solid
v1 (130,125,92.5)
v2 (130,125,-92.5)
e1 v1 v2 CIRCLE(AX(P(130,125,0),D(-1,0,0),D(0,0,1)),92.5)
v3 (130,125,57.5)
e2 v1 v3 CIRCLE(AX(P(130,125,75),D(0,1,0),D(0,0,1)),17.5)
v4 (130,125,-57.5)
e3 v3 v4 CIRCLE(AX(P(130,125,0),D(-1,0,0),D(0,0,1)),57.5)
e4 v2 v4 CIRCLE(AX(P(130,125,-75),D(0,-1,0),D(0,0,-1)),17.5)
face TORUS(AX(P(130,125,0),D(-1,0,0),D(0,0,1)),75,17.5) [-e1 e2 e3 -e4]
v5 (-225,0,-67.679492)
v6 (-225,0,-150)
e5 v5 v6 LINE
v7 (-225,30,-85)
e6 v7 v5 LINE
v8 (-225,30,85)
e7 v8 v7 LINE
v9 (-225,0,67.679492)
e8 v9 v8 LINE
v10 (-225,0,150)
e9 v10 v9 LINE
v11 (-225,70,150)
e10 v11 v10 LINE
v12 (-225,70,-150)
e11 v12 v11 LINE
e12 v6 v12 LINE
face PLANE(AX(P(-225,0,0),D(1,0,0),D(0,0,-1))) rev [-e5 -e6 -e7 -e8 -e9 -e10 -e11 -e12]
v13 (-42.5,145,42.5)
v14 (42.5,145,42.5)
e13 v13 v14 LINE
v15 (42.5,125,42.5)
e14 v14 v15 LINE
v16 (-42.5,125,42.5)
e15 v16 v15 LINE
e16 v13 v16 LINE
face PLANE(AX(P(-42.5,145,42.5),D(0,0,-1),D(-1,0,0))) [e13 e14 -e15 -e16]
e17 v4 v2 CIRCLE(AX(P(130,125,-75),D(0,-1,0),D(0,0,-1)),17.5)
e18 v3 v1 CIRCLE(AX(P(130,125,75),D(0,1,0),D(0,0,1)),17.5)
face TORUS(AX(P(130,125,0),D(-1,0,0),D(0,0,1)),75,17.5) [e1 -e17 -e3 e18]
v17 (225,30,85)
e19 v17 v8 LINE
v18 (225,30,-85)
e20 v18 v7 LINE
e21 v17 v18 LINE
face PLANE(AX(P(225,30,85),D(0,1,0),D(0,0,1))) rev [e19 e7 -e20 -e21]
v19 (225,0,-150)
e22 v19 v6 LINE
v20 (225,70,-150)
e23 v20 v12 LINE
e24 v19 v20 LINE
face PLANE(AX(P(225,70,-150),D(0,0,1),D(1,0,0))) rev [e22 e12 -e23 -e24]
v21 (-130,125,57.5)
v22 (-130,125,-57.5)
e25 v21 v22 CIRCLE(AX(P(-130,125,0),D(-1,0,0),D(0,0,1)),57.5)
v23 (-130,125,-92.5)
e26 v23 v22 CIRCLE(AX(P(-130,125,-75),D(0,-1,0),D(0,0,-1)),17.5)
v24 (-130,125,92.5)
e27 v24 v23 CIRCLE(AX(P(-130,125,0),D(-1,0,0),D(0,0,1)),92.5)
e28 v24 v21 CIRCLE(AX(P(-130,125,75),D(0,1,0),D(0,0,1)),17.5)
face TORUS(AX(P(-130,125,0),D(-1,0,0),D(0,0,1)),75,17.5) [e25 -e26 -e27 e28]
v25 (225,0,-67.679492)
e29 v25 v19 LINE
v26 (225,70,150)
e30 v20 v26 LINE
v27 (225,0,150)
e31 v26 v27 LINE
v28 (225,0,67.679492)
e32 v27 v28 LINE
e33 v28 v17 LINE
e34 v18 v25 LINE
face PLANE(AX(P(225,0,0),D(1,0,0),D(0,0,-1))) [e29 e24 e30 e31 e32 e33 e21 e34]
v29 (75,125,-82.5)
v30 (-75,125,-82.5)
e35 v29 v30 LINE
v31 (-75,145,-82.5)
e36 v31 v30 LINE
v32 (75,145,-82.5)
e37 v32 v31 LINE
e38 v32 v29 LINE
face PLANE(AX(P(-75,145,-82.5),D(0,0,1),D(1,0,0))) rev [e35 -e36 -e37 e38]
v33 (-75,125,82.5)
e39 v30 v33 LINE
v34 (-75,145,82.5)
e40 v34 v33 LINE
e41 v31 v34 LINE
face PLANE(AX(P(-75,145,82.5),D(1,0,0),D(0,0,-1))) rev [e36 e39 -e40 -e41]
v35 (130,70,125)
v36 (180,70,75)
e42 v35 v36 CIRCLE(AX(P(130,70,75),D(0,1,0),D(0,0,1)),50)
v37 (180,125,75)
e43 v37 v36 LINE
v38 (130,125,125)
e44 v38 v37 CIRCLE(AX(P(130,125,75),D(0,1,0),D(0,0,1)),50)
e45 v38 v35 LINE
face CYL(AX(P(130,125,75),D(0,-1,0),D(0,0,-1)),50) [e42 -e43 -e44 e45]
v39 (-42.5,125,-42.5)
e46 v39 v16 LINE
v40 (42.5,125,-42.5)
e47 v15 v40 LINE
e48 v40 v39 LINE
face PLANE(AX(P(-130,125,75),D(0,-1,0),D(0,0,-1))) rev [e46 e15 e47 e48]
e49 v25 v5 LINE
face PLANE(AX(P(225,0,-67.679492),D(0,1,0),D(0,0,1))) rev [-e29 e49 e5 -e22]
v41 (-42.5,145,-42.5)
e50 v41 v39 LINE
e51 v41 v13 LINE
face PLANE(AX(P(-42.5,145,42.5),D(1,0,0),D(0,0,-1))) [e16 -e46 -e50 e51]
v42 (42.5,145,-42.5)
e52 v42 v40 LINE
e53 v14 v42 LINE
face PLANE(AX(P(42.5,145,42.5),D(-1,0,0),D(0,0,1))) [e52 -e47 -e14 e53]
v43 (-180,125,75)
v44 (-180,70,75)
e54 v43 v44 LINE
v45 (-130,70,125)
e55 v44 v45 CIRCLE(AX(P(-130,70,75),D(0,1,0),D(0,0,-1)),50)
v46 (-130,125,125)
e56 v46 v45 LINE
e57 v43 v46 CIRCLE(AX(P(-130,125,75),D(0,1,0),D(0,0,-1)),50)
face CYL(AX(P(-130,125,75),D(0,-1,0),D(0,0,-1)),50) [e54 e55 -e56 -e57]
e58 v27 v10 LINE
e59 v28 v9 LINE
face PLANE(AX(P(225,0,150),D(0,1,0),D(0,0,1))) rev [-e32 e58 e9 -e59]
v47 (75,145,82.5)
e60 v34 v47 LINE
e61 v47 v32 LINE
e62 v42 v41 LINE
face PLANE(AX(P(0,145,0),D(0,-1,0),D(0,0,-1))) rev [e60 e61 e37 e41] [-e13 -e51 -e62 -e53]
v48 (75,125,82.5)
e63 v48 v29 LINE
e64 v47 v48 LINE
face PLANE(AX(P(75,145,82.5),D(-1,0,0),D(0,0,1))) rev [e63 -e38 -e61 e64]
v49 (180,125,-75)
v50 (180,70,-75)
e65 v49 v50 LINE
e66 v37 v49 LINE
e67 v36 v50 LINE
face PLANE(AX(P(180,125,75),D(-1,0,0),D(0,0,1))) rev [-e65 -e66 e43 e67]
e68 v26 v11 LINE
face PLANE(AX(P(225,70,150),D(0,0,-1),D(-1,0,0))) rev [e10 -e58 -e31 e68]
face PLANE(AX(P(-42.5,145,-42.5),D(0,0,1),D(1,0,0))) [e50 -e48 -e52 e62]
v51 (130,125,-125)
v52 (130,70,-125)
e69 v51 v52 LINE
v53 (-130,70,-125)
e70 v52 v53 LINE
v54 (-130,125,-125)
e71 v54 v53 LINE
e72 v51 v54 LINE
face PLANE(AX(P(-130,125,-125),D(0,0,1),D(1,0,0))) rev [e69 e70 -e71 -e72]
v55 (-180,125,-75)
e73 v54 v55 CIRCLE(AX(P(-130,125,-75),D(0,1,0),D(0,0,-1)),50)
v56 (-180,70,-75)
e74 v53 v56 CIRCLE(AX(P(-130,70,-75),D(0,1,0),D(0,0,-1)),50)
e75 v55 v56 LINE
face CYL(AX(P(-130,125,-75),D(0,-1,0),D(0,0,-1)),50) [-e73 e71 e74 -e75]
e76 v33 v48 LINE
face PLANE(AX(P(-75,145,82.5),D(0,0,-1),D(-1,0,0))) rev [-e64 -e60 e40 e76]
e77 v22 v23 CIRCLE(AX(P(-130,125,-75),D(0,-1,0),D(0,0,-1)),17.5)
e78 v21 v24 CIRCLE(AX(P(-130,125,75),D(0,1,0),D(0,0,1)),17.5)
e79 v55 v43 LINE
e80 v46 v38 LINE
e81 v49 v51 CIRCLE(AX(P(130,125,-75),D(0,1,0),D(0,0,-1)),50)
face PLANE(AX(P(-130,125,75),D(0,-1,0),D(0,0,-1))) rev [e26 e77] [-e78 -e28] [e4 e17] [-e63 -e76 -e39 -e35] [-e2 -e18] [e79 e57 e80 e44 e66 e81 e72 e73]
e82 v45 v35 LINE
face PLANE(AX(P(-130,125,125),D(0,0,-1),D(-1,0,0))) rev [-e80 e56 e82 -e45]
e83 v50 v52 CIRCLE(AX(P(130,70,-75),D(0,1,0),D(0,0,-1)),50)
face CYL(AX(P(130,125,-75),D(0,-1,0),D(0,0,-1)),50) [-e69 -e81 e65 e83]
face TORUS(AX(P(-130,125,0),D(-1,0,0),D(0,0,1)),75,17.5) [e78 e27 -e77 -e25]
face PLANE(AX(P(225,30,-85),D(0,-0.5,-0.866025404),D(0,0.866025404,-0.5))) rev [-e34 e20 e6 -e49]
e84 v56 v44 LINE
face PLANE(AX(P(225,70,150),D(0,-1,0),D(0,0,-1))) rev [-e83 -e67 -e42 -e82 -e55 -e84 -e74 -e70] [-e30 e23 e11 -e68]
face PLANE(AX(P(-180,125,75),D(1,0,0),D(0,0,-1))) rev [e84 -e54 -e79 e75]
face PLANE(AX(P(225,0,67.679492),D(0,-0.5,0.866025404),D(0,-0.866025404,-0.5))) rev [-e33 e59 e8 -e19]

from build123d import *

# Parameters (mm, degrees)
BASE_BLOCK_V_GROOVE_DEPTH   = 225
TOP_PAD_360X250_DEPTH       = 55
SQUARE_FRAME_SKETCH_150_W   = 150
SQUARE_FRAME_SKETCH_150_H   = 165
SQUARE_FRAME_SKETCH_150_W_2 = 85
SQUARE_FRAME_SKETCH_150_H_2 = 85
SQUARE_FRAME_BOSS_150_DEPTH = 20
LIFTING_HANDLE_35_PROFILE_R = 17.5


with BuildPart() as part:
    # Base V-Groove Profile Sketch → Base Block V-Groove (new, symmetric)
    with BuildSketch(Plane(origin=(0, 0, 0), x_dir=(0, 0, -1), z_dir=(1, 0, 0))):
        Polygon((-67.679491924, 0), (-85, 30), (85, 30), (67.679491924, 0), (150, 0), (150, 70), (-150, 70), (-150, 0), align=None)
    extrude(amount=BASE_BLOCK_V_GROOVE_DEPTH, both=True)

    # Top Pad Sketch 360x250 → Top Pad 360x250 (add)
    with BuildSketch(Plane(origin=(0, 70, 0), x_dir=(1, 0, 0), z_dir=(0, 1, 0))):
        with BuildLine():
            Line((-130, -125), (130, -125))
            ThreePointArc((130, -125), (165.355339059, -110.355339059), (180, -75))
            Line((180, -75), (180, 75))
            ThreePointArc((180, 75), (165.355339059, 110.355339059), (130, 125))
            Line((130, 125), (-130, 125))
            ThreePointArc((-130, 125), (-165.355339059, 110.355339059), (-180, 75))
            Line((-180, 75), (-180, -75))
            ThreePointArc((-180, -75), (-165.355339059, -110.355339059), (-130, -125))
        make_face()
    extrude(amount=TOP_PAD_360X250_DEPTH)

    # Square Frame Sketch 150 → Square Frame Boss 150 (add)
    with BuildSketch(Plane(origin=(0, 125, 0), x_dir=(1, 0, 0), z_dir=(0, 1, 0))):
        Rectangle(SQUARE_FRAME_SKETCH_150_W, SQUARE_FRAME_SKETCH_150_H)
        Rectangle(SQUARE_FRAME_SKETCH_150_W_2, SQUARE_FRAME_SKETCH_150_H_2, mode=Mode.SUBTRACT)
    extrude(amount=SQUARE_FRAME_BOSS_150_DEPTH)

    # Lifting Handle Ø35: sweep along a path in Handle Path Sketch
    with BuildLine(Plane(origin=(130, 0, 0), x_dir=(0, 0, -1), z_dir=(1, 0, 0))) as lifting_handle_35_path:
        ThreePointArc((-75, 125), (0, 200), (75, 125))
    # Lifting Handle Ø35 profile (on start of the path) → Lifting Handle Ø35 (sweep)
    with BuildSketch(Plane(origin=(130, 125, 75), x_dir=(0, 0, 1), z_dir=(0, 1, 0))):
        Circle(LIFTING_HANDLE_35_PROFILE_R)
    lifting_handle_35 = sweep(path=lifting_handle_35_path.line)

    # Lifting Handle Mirror: Lifting Handle Ø35 across plane
    add(lifting_handle_35.mirror(Plane(origin=(0, 0, 0), x_dir=(0, 0, 1), z_dir=(1, 0, 0))))


solid = part.part
